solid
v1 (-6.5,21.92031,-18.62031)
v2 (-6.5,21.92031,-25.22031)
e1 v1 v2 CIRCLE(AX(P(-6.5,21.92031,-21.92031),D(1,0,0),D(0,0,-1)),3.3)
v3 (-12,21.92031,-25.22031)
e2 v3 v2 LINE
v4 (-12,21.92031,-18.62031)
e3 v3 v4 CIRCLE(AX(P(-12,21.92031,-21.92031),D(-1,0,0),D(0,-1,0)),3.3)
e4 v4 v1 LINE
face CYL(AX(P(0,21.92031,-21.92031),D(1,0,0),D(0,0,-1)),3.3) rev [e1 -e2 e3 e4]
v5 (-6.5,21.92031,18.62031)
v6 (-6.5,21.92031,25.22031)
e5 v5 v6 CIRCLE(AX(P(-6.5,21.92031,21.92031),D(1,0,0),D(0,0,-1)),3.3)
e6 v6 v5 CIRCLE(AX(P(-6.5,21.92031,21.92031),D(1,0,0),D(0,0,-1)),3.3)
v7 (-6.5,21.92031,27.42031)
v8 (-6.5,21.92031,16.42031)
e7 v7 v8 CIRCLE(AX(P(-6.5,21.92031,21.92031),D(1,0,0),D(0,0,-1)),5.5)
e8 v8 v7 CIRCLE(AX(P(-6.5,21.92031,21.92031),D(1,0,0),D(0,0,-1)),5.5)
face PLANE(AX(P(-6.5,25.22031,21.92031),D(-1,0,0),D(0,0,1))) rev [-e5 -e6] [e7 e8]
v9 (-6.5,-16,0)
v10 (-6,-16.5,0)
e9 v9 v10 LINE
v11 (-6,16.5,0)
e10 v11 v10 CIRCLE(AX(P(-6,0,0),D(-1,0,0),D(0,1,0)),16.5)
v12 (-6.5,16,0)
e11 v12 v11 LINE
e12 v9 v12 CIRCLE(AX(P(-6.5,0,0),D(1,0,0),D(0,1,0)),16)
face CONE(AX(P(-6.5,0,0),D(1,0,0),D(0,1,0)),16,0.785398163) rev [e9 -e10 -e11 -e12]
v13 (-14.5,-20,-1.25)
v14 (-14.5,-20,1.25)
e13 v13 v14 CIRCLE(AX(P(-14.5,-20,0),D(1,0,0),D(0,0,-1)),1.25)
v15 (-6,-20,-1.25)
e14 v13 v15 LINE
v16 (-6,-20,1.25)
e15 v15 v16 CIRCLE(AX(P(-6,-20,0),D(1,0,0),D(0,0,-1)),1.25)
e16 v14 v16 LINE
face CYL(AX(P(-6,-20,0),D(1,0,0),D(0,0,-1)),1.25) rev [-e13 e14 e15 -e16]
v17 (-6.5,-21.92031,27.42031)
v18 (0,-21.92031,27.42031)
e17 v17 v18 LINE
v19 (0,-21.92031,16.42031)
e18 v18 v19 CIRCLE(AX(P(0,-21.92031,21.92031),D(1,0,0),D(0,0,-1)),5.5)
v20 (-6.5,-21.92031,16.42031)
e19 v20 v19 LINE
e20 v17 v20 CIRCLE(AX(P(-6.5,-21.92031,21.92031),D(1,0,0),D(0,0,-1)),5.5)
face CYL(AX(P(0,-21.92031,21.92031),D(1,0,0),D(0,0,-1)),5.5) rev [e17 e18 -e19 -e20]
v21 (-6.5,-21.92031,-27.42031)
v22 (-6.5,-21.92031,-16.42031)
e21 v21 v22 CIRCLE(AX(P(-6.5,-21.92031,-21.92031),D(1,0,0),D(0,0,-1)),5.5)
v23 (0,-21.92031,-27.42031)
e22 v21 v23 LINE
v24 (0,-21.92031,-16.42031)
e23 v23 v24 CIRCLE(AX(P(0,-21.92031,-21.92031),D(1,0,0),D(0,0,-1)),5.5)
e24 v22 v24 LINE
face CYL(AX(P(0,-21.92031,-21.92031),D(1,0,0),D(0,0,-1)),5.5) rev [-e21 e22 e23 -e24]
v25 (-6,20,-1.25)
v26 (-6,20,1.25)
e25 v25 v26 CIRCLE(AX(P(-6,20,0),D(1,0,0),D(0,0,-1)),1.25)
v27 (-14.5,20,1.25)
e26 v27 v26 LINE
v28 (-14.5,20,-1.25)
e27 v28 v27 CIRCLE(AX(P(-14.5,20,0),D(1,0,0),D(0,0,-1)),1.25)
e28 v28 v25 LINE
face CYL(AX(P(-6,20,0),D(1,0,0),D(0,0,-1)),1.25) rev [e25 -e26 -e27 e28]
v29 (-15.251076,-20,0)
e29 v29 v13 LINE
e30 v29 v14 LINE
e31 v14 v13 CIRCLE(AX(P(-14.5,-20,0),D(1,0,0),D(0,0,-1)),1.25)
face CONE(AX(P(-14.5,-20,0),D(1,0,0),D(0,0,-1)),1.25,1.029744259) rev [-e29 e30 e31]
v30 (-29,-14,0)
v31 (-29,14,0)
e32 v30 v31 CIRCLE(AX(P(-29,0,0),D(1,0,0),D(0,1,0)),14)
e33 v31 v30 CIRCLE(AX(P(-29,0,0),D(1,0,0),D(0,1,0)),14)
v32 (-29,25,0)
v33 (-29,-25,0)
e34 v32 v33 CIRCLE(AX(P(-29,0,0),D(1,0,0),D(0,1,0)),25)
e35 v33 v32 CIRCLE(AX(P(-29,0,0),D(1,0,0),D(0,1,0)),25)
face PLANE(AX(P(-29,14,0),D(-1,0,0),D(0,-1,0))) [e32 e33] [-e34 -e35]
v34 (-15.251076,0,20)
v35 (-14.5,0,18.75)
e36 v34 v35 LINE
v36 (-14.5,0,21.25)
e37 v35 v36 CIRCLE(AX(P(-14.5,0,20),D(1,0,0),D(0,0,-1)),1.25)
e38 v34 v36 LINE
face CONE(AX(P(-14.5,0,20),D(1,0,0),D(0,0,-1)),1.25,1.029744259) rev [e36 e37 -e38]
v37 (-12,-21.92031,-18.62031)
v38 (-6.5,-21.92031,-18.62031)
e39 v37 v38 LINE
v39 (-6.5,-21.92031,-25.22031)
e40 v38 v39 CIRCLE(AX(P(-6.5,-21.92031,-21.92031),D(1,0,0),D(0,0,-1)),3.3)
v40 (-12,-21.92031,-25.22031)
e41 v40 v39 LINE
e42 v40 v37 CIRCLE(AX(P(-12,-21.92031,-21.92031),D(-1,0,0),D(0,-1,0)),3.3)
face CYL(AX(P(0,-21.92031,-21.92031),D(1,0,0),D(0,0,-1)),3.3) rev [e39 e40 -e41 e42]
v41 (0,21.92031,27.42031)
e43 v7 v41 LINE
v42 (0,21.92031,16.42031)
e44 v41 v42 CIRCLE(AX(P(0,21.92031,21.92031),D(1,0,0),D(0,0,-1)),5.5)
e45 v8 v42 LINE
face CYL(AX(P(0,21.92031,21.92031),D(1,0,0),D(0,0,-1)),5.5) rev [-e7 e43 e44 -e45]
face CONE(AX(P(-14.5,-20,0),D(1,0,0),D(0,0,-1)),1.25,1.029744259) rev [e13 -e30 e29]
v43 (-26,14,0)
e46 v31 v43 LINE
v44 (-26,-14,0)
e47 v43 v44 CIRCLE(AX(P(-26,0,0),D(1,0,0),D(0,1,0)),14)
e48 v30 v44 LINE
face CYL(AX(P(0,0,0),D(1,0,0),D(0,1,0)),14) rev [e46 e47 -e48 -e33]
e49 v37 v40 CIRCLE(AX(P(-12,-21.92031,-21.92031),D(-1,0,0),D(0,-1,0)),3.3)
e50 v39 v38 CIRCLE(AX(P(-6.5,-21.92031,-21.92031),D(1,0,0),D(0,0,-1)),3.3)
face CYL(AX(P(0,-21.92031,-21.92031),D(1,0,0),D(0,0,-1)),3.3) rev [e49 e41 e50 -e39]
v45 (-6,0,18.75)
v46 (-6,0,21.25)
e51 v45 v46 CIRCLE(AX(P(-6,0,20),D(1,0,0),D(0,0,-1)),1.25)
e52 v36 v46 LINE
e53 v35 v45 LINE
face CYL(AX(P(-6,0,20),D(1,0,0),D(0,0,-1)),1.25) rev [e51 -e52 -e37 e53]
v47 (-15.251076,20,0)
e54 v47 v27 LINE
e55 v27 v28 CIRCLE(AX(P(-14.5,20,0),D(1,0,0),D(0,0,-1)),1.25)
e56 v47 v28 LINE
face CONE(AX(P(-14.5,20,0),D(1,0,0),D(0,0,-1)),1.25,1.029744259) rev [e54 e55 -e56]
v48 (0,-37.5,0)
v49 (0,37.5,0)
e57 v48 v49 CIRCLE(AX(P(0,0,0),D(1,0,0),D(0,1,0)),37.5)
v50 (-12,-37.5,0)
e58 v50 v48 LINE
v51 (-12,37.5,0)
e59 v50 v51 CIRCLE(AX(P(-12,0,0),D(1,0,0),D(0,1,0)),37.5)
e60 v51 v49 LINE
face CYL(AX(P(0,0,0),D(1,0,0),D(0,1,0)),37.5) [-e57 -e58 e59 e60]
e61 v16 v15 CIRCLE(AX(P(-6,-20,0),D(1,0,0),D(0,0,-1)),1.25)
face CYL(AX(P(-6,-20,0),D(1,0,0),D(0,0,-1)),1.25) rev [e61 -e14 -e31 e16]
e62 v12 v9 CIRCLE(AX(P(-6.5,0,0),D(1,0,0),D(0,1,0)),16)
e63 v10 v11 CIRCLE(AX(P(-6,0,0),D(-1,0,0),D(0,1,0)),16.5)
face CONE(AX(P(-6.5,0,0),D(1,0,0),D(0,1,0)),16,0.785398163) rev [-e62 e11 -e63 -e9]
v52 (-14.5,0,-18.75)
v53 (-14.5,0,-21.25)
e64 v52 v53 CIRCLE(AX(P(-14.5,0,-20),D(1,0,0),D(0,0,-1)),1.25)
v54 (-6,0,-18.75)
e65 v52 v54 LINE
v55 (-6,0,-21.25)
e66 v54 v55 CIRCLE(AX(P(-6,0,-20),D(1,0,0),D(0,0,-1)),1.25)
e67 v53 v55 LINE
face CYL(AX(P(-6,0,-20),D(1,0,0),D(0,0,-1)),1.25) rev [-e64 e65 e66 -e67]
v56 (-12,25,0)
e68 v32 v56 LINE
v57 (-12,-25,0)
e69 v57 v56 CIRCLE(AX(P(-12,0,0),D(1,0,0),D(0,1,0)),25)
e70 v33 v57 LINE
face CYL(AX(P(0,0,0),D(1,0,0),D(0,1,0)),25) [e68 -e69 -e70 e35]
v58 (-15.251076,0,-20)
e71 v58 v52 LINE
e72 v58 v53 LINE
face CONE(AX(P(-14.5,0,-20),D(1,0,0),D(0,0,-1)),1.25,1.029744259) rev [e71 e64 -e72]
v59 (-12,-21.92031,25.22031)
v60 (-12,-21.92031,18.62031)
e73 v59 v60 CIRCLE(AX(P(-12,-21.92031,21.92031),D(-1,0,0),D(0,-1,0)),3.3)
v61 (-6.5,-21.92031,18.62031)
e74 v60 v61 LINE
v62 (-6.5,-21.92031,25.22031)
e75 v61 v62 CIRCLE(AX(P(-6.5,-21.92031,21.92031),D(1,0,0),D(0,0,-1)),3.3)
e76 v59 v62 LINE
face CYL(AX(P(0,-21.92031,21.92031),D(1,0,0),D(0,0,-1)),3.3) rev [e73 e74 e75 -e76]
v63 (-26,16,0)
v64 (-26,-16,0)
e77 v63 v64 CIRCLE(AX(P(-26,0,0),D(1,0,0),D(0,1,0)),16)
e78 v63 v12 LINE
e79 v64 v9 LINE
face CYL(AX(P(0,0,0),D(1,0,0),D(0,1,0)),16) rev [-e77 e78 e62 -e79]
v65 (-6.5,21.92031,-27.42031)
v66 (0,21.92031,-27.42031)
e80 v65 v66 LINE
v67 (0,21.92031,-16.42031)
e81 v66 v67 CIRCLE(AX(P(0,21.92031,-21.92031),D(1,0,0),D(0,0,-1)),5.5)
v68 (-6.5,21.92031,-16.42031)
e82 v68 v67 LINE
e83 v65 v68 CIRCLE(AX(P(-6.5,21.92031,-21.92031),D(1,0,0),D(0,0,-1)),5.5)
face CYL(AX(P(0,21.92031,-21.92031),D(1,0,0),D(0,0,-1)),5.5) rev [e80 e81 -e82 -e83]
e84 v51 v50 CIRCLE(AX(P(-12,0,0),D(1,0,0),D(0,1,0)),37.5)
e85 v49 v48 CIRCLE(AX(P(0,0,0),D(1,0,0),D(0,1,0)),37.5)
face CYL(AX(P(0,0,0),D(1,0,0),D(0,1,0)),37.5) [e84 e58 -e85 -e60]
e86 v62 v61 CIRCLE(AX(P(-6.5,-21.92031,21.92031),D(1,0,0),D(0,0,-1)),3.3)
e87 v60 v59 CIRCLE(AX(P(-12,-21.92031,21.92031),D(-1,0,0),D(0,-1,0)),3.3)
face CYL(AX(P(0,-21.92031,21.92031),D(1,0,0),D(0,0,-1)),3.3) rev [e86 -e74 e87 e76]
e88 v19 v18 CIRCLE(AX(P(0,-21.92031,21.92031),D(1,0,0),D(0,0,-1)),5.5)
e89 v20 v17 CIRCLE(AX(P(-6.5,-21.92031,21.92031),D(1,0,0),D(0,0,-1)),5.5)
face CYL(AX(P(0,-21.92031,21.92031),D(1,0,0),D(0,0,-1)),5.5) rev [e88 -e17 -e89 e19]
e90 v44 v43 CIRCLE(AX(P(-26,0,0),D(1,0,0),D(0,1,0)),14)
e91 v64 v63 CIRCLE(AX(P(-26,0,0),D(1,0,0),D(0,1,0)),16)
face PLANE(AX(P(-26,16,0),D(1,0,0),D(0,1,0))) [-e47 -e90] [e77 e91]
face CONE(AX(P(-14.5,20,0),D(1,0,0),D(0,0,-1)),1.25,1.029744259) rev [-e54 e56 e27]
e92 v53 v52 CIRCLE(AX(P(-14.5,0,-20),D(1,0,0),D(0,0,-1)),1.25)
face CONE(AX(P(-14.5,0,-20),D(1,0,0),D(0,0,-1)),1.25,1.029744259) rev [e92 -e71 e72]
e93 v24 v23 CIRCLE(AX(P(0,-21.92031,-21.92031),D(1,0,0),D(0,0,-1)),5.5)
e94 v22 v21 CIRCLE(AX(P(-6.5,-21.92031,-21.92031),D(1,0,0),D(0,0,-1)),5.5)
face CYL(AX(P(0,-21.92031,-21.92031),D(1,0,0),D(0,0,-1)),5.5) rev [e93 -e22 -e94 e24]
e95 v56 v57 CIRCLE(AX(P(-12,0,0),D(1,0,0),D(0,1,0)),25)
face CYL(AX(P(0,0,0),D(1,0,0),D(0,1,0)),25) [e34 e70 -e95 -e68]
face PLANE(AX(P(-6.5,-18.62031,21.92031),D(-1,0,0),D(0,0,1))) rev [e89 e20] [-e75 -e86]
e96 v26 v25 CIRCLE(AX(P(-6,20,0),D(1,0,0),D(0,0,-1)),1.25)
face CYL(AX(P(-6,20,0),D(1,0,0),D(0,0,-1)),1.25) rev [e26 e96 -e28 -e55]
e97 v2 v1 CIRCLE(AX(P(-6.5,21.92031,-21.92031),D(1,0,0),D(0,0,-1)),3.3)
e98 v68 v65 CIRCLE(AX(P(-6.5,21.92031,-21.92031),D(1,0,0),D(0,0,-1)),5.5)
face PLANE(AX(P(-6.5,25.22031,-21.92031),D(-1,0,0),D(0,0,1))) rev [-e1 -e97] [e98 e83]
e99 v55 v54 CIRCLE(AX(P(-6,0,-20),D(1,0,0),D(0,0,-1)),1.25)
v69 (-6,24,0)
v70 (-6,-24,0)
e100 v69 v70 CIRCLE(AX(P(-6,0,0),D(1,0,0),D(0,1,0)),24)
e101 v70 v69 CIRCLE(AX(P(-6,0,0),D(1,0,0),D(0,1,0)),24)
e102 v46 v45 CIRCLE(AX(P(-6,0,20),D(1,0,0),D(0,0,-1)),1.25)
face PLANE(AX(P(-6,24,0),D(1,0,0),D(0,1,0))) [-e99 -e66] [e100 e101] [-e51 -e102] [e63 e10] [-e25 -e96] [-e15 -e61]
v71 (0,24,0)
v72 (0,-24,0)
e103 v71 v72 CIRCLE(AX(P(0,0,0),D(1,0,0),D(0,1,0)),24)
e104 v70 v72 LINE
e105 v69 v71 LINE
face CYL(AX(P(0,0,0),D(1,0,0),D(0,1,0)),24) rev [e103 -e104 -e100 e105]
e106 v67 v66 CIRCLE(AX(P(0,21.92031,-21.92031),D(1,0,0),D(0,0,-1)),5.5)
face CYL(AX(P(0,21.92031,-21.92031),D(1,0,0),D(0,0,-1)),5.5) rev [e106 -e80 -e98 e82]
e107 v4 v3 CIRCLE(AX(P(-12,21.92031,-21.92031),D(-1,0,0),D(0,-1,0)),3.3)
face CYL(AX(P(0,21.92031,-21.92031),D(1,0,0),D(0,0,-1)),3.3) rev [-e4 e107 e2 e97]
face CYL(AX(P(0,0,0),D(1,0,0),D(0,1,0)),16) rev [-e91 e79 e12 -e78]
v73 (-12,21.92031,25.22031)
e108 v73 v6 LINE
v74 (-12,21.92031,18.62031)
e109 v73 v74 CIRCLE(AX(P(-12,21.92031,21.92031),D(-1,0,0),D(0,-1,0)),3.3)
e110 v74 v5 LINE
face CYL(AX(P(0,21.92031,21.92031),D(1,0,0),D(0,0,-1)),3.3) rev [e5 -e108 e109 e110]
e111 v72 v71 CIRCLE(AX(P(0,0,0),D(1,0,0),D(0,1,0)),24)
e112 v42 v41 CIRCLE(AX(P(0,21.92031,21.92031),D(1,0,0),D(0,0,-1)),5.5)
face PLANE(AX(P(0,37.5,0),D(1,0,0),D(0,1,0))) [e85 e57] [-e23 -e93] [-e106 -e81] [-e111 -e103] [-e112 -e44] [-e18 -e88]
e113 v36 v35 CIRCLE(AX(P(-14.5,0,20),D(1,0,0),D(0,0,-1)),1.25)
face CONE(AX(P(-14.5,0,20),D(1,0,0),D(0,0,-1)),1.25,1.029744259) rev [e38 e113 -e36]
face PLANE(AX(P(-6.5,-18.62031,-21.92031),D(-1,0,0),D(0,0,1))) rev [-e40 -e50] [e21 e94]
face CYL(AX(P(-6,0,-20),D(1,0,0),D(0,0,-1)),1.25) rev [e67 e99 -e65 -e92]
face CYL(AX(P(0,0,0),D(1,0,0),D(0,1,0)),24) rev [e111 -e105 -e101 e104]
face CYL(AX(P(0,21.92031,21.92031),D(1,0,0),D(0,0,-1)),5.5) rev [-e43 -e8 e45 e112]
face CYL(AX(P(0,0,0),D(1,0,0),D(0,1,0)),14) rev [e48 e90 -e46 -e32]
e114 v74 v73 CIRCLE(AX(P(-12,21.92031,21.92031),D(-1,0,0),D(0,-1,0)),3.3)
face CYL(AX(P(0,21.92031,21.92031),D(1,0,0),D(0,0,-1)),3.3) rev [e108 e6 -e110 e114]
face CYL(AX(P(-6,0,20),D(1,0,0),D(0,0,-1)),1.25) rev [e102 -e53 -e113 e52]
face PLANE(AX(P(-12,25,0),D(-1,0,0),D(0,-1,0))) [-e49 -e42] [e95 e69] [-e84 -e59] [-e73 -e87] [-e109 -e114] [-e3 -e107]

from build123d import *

# Parameters (mm, degrees)
CBORE_SOCKET_HEAD_CAP_SCREW1_D           = 6.6
CBORE_SOCKET_HEAD_CAP_SCREW1_CBORE_D     = 11
CBORE_SOCKET_HEAD_CAP_SCREW1_CBORE_DEPTH = 6.5
TAPPED_HOLE1_D                           = 2.5
TAPPED_HOLE1_DEPTH                       = 8.5
TAPPED_HOLE1_TIP                         = 0.751075774
CHAMFER1_SIZE                            = 0.5


with BuildPart() as part:
    # Sketch1 → Revolve1 (revolve)
    with BuildSketch(Plane.XY):
        Polygon((0, 24), (-6, 24), (-6, 16), (-26, 16), (-26, 14), (-29, 14), (-29, 25), (-12, 25), (-12, 37.5), (0, 37.5), align=None)
    revolve(axis=Axis((0, 0, 0), (-1, 0, 0)))

    # CBORE Socket Head Cap Screw1 (through all)
    with Locations(Plane(origin=(0, 0, 0), x_dir=(0, 0, -1), z_dir=(1, 0, 0))):
        with Locations((-21.920310217, 21.920310217), (21.920310217, 21.920310217), (21.920310217, -21.920310217), (-21.920310217, -21.920310217)):
            CounterBoreHole(CBORE_SOCKET_HEAD_CAP_SCREW1_D / 2, CBORE_SOCKET_HEAD_CAP_SCREW1_CBORE_D / 2, CBORE_SOCKET_HEAD_CAP_SCREW1_CBORE_DEPTH)

    # Tapped Hole1
    with Locations(Plane(origin=(-6, 0, 0), x_dir=(0, 0, -1), z_dir=(1, 0, 0))):
        with Locations((0, 20), (-20, 0), (0, -20), (20, 0)):
            Hole(TAPPED_HOLE1_D / 2, depth=TAPPED_HOLE1_DEPTH)
            with Locations((0, 0, -(TAPPED_HOLE1_DEPTH + TAPPED_HOLE1_TIP / 2))):  # 118° drill point
                Cone(0, TAPPED_HOLE1_D / 2, TAPPED_HOLE1_TIP, mode=Mode.SUBTRACT)

    # Chamfer1
    chamfer1_edges = [part.edges().sort_by_distance(p)[0] for p in [
        (-6, -16, 0),
    ]]
    chamfer(chamfer1_edges, length=CHAMFER1_SIZE)


solid = part.part
